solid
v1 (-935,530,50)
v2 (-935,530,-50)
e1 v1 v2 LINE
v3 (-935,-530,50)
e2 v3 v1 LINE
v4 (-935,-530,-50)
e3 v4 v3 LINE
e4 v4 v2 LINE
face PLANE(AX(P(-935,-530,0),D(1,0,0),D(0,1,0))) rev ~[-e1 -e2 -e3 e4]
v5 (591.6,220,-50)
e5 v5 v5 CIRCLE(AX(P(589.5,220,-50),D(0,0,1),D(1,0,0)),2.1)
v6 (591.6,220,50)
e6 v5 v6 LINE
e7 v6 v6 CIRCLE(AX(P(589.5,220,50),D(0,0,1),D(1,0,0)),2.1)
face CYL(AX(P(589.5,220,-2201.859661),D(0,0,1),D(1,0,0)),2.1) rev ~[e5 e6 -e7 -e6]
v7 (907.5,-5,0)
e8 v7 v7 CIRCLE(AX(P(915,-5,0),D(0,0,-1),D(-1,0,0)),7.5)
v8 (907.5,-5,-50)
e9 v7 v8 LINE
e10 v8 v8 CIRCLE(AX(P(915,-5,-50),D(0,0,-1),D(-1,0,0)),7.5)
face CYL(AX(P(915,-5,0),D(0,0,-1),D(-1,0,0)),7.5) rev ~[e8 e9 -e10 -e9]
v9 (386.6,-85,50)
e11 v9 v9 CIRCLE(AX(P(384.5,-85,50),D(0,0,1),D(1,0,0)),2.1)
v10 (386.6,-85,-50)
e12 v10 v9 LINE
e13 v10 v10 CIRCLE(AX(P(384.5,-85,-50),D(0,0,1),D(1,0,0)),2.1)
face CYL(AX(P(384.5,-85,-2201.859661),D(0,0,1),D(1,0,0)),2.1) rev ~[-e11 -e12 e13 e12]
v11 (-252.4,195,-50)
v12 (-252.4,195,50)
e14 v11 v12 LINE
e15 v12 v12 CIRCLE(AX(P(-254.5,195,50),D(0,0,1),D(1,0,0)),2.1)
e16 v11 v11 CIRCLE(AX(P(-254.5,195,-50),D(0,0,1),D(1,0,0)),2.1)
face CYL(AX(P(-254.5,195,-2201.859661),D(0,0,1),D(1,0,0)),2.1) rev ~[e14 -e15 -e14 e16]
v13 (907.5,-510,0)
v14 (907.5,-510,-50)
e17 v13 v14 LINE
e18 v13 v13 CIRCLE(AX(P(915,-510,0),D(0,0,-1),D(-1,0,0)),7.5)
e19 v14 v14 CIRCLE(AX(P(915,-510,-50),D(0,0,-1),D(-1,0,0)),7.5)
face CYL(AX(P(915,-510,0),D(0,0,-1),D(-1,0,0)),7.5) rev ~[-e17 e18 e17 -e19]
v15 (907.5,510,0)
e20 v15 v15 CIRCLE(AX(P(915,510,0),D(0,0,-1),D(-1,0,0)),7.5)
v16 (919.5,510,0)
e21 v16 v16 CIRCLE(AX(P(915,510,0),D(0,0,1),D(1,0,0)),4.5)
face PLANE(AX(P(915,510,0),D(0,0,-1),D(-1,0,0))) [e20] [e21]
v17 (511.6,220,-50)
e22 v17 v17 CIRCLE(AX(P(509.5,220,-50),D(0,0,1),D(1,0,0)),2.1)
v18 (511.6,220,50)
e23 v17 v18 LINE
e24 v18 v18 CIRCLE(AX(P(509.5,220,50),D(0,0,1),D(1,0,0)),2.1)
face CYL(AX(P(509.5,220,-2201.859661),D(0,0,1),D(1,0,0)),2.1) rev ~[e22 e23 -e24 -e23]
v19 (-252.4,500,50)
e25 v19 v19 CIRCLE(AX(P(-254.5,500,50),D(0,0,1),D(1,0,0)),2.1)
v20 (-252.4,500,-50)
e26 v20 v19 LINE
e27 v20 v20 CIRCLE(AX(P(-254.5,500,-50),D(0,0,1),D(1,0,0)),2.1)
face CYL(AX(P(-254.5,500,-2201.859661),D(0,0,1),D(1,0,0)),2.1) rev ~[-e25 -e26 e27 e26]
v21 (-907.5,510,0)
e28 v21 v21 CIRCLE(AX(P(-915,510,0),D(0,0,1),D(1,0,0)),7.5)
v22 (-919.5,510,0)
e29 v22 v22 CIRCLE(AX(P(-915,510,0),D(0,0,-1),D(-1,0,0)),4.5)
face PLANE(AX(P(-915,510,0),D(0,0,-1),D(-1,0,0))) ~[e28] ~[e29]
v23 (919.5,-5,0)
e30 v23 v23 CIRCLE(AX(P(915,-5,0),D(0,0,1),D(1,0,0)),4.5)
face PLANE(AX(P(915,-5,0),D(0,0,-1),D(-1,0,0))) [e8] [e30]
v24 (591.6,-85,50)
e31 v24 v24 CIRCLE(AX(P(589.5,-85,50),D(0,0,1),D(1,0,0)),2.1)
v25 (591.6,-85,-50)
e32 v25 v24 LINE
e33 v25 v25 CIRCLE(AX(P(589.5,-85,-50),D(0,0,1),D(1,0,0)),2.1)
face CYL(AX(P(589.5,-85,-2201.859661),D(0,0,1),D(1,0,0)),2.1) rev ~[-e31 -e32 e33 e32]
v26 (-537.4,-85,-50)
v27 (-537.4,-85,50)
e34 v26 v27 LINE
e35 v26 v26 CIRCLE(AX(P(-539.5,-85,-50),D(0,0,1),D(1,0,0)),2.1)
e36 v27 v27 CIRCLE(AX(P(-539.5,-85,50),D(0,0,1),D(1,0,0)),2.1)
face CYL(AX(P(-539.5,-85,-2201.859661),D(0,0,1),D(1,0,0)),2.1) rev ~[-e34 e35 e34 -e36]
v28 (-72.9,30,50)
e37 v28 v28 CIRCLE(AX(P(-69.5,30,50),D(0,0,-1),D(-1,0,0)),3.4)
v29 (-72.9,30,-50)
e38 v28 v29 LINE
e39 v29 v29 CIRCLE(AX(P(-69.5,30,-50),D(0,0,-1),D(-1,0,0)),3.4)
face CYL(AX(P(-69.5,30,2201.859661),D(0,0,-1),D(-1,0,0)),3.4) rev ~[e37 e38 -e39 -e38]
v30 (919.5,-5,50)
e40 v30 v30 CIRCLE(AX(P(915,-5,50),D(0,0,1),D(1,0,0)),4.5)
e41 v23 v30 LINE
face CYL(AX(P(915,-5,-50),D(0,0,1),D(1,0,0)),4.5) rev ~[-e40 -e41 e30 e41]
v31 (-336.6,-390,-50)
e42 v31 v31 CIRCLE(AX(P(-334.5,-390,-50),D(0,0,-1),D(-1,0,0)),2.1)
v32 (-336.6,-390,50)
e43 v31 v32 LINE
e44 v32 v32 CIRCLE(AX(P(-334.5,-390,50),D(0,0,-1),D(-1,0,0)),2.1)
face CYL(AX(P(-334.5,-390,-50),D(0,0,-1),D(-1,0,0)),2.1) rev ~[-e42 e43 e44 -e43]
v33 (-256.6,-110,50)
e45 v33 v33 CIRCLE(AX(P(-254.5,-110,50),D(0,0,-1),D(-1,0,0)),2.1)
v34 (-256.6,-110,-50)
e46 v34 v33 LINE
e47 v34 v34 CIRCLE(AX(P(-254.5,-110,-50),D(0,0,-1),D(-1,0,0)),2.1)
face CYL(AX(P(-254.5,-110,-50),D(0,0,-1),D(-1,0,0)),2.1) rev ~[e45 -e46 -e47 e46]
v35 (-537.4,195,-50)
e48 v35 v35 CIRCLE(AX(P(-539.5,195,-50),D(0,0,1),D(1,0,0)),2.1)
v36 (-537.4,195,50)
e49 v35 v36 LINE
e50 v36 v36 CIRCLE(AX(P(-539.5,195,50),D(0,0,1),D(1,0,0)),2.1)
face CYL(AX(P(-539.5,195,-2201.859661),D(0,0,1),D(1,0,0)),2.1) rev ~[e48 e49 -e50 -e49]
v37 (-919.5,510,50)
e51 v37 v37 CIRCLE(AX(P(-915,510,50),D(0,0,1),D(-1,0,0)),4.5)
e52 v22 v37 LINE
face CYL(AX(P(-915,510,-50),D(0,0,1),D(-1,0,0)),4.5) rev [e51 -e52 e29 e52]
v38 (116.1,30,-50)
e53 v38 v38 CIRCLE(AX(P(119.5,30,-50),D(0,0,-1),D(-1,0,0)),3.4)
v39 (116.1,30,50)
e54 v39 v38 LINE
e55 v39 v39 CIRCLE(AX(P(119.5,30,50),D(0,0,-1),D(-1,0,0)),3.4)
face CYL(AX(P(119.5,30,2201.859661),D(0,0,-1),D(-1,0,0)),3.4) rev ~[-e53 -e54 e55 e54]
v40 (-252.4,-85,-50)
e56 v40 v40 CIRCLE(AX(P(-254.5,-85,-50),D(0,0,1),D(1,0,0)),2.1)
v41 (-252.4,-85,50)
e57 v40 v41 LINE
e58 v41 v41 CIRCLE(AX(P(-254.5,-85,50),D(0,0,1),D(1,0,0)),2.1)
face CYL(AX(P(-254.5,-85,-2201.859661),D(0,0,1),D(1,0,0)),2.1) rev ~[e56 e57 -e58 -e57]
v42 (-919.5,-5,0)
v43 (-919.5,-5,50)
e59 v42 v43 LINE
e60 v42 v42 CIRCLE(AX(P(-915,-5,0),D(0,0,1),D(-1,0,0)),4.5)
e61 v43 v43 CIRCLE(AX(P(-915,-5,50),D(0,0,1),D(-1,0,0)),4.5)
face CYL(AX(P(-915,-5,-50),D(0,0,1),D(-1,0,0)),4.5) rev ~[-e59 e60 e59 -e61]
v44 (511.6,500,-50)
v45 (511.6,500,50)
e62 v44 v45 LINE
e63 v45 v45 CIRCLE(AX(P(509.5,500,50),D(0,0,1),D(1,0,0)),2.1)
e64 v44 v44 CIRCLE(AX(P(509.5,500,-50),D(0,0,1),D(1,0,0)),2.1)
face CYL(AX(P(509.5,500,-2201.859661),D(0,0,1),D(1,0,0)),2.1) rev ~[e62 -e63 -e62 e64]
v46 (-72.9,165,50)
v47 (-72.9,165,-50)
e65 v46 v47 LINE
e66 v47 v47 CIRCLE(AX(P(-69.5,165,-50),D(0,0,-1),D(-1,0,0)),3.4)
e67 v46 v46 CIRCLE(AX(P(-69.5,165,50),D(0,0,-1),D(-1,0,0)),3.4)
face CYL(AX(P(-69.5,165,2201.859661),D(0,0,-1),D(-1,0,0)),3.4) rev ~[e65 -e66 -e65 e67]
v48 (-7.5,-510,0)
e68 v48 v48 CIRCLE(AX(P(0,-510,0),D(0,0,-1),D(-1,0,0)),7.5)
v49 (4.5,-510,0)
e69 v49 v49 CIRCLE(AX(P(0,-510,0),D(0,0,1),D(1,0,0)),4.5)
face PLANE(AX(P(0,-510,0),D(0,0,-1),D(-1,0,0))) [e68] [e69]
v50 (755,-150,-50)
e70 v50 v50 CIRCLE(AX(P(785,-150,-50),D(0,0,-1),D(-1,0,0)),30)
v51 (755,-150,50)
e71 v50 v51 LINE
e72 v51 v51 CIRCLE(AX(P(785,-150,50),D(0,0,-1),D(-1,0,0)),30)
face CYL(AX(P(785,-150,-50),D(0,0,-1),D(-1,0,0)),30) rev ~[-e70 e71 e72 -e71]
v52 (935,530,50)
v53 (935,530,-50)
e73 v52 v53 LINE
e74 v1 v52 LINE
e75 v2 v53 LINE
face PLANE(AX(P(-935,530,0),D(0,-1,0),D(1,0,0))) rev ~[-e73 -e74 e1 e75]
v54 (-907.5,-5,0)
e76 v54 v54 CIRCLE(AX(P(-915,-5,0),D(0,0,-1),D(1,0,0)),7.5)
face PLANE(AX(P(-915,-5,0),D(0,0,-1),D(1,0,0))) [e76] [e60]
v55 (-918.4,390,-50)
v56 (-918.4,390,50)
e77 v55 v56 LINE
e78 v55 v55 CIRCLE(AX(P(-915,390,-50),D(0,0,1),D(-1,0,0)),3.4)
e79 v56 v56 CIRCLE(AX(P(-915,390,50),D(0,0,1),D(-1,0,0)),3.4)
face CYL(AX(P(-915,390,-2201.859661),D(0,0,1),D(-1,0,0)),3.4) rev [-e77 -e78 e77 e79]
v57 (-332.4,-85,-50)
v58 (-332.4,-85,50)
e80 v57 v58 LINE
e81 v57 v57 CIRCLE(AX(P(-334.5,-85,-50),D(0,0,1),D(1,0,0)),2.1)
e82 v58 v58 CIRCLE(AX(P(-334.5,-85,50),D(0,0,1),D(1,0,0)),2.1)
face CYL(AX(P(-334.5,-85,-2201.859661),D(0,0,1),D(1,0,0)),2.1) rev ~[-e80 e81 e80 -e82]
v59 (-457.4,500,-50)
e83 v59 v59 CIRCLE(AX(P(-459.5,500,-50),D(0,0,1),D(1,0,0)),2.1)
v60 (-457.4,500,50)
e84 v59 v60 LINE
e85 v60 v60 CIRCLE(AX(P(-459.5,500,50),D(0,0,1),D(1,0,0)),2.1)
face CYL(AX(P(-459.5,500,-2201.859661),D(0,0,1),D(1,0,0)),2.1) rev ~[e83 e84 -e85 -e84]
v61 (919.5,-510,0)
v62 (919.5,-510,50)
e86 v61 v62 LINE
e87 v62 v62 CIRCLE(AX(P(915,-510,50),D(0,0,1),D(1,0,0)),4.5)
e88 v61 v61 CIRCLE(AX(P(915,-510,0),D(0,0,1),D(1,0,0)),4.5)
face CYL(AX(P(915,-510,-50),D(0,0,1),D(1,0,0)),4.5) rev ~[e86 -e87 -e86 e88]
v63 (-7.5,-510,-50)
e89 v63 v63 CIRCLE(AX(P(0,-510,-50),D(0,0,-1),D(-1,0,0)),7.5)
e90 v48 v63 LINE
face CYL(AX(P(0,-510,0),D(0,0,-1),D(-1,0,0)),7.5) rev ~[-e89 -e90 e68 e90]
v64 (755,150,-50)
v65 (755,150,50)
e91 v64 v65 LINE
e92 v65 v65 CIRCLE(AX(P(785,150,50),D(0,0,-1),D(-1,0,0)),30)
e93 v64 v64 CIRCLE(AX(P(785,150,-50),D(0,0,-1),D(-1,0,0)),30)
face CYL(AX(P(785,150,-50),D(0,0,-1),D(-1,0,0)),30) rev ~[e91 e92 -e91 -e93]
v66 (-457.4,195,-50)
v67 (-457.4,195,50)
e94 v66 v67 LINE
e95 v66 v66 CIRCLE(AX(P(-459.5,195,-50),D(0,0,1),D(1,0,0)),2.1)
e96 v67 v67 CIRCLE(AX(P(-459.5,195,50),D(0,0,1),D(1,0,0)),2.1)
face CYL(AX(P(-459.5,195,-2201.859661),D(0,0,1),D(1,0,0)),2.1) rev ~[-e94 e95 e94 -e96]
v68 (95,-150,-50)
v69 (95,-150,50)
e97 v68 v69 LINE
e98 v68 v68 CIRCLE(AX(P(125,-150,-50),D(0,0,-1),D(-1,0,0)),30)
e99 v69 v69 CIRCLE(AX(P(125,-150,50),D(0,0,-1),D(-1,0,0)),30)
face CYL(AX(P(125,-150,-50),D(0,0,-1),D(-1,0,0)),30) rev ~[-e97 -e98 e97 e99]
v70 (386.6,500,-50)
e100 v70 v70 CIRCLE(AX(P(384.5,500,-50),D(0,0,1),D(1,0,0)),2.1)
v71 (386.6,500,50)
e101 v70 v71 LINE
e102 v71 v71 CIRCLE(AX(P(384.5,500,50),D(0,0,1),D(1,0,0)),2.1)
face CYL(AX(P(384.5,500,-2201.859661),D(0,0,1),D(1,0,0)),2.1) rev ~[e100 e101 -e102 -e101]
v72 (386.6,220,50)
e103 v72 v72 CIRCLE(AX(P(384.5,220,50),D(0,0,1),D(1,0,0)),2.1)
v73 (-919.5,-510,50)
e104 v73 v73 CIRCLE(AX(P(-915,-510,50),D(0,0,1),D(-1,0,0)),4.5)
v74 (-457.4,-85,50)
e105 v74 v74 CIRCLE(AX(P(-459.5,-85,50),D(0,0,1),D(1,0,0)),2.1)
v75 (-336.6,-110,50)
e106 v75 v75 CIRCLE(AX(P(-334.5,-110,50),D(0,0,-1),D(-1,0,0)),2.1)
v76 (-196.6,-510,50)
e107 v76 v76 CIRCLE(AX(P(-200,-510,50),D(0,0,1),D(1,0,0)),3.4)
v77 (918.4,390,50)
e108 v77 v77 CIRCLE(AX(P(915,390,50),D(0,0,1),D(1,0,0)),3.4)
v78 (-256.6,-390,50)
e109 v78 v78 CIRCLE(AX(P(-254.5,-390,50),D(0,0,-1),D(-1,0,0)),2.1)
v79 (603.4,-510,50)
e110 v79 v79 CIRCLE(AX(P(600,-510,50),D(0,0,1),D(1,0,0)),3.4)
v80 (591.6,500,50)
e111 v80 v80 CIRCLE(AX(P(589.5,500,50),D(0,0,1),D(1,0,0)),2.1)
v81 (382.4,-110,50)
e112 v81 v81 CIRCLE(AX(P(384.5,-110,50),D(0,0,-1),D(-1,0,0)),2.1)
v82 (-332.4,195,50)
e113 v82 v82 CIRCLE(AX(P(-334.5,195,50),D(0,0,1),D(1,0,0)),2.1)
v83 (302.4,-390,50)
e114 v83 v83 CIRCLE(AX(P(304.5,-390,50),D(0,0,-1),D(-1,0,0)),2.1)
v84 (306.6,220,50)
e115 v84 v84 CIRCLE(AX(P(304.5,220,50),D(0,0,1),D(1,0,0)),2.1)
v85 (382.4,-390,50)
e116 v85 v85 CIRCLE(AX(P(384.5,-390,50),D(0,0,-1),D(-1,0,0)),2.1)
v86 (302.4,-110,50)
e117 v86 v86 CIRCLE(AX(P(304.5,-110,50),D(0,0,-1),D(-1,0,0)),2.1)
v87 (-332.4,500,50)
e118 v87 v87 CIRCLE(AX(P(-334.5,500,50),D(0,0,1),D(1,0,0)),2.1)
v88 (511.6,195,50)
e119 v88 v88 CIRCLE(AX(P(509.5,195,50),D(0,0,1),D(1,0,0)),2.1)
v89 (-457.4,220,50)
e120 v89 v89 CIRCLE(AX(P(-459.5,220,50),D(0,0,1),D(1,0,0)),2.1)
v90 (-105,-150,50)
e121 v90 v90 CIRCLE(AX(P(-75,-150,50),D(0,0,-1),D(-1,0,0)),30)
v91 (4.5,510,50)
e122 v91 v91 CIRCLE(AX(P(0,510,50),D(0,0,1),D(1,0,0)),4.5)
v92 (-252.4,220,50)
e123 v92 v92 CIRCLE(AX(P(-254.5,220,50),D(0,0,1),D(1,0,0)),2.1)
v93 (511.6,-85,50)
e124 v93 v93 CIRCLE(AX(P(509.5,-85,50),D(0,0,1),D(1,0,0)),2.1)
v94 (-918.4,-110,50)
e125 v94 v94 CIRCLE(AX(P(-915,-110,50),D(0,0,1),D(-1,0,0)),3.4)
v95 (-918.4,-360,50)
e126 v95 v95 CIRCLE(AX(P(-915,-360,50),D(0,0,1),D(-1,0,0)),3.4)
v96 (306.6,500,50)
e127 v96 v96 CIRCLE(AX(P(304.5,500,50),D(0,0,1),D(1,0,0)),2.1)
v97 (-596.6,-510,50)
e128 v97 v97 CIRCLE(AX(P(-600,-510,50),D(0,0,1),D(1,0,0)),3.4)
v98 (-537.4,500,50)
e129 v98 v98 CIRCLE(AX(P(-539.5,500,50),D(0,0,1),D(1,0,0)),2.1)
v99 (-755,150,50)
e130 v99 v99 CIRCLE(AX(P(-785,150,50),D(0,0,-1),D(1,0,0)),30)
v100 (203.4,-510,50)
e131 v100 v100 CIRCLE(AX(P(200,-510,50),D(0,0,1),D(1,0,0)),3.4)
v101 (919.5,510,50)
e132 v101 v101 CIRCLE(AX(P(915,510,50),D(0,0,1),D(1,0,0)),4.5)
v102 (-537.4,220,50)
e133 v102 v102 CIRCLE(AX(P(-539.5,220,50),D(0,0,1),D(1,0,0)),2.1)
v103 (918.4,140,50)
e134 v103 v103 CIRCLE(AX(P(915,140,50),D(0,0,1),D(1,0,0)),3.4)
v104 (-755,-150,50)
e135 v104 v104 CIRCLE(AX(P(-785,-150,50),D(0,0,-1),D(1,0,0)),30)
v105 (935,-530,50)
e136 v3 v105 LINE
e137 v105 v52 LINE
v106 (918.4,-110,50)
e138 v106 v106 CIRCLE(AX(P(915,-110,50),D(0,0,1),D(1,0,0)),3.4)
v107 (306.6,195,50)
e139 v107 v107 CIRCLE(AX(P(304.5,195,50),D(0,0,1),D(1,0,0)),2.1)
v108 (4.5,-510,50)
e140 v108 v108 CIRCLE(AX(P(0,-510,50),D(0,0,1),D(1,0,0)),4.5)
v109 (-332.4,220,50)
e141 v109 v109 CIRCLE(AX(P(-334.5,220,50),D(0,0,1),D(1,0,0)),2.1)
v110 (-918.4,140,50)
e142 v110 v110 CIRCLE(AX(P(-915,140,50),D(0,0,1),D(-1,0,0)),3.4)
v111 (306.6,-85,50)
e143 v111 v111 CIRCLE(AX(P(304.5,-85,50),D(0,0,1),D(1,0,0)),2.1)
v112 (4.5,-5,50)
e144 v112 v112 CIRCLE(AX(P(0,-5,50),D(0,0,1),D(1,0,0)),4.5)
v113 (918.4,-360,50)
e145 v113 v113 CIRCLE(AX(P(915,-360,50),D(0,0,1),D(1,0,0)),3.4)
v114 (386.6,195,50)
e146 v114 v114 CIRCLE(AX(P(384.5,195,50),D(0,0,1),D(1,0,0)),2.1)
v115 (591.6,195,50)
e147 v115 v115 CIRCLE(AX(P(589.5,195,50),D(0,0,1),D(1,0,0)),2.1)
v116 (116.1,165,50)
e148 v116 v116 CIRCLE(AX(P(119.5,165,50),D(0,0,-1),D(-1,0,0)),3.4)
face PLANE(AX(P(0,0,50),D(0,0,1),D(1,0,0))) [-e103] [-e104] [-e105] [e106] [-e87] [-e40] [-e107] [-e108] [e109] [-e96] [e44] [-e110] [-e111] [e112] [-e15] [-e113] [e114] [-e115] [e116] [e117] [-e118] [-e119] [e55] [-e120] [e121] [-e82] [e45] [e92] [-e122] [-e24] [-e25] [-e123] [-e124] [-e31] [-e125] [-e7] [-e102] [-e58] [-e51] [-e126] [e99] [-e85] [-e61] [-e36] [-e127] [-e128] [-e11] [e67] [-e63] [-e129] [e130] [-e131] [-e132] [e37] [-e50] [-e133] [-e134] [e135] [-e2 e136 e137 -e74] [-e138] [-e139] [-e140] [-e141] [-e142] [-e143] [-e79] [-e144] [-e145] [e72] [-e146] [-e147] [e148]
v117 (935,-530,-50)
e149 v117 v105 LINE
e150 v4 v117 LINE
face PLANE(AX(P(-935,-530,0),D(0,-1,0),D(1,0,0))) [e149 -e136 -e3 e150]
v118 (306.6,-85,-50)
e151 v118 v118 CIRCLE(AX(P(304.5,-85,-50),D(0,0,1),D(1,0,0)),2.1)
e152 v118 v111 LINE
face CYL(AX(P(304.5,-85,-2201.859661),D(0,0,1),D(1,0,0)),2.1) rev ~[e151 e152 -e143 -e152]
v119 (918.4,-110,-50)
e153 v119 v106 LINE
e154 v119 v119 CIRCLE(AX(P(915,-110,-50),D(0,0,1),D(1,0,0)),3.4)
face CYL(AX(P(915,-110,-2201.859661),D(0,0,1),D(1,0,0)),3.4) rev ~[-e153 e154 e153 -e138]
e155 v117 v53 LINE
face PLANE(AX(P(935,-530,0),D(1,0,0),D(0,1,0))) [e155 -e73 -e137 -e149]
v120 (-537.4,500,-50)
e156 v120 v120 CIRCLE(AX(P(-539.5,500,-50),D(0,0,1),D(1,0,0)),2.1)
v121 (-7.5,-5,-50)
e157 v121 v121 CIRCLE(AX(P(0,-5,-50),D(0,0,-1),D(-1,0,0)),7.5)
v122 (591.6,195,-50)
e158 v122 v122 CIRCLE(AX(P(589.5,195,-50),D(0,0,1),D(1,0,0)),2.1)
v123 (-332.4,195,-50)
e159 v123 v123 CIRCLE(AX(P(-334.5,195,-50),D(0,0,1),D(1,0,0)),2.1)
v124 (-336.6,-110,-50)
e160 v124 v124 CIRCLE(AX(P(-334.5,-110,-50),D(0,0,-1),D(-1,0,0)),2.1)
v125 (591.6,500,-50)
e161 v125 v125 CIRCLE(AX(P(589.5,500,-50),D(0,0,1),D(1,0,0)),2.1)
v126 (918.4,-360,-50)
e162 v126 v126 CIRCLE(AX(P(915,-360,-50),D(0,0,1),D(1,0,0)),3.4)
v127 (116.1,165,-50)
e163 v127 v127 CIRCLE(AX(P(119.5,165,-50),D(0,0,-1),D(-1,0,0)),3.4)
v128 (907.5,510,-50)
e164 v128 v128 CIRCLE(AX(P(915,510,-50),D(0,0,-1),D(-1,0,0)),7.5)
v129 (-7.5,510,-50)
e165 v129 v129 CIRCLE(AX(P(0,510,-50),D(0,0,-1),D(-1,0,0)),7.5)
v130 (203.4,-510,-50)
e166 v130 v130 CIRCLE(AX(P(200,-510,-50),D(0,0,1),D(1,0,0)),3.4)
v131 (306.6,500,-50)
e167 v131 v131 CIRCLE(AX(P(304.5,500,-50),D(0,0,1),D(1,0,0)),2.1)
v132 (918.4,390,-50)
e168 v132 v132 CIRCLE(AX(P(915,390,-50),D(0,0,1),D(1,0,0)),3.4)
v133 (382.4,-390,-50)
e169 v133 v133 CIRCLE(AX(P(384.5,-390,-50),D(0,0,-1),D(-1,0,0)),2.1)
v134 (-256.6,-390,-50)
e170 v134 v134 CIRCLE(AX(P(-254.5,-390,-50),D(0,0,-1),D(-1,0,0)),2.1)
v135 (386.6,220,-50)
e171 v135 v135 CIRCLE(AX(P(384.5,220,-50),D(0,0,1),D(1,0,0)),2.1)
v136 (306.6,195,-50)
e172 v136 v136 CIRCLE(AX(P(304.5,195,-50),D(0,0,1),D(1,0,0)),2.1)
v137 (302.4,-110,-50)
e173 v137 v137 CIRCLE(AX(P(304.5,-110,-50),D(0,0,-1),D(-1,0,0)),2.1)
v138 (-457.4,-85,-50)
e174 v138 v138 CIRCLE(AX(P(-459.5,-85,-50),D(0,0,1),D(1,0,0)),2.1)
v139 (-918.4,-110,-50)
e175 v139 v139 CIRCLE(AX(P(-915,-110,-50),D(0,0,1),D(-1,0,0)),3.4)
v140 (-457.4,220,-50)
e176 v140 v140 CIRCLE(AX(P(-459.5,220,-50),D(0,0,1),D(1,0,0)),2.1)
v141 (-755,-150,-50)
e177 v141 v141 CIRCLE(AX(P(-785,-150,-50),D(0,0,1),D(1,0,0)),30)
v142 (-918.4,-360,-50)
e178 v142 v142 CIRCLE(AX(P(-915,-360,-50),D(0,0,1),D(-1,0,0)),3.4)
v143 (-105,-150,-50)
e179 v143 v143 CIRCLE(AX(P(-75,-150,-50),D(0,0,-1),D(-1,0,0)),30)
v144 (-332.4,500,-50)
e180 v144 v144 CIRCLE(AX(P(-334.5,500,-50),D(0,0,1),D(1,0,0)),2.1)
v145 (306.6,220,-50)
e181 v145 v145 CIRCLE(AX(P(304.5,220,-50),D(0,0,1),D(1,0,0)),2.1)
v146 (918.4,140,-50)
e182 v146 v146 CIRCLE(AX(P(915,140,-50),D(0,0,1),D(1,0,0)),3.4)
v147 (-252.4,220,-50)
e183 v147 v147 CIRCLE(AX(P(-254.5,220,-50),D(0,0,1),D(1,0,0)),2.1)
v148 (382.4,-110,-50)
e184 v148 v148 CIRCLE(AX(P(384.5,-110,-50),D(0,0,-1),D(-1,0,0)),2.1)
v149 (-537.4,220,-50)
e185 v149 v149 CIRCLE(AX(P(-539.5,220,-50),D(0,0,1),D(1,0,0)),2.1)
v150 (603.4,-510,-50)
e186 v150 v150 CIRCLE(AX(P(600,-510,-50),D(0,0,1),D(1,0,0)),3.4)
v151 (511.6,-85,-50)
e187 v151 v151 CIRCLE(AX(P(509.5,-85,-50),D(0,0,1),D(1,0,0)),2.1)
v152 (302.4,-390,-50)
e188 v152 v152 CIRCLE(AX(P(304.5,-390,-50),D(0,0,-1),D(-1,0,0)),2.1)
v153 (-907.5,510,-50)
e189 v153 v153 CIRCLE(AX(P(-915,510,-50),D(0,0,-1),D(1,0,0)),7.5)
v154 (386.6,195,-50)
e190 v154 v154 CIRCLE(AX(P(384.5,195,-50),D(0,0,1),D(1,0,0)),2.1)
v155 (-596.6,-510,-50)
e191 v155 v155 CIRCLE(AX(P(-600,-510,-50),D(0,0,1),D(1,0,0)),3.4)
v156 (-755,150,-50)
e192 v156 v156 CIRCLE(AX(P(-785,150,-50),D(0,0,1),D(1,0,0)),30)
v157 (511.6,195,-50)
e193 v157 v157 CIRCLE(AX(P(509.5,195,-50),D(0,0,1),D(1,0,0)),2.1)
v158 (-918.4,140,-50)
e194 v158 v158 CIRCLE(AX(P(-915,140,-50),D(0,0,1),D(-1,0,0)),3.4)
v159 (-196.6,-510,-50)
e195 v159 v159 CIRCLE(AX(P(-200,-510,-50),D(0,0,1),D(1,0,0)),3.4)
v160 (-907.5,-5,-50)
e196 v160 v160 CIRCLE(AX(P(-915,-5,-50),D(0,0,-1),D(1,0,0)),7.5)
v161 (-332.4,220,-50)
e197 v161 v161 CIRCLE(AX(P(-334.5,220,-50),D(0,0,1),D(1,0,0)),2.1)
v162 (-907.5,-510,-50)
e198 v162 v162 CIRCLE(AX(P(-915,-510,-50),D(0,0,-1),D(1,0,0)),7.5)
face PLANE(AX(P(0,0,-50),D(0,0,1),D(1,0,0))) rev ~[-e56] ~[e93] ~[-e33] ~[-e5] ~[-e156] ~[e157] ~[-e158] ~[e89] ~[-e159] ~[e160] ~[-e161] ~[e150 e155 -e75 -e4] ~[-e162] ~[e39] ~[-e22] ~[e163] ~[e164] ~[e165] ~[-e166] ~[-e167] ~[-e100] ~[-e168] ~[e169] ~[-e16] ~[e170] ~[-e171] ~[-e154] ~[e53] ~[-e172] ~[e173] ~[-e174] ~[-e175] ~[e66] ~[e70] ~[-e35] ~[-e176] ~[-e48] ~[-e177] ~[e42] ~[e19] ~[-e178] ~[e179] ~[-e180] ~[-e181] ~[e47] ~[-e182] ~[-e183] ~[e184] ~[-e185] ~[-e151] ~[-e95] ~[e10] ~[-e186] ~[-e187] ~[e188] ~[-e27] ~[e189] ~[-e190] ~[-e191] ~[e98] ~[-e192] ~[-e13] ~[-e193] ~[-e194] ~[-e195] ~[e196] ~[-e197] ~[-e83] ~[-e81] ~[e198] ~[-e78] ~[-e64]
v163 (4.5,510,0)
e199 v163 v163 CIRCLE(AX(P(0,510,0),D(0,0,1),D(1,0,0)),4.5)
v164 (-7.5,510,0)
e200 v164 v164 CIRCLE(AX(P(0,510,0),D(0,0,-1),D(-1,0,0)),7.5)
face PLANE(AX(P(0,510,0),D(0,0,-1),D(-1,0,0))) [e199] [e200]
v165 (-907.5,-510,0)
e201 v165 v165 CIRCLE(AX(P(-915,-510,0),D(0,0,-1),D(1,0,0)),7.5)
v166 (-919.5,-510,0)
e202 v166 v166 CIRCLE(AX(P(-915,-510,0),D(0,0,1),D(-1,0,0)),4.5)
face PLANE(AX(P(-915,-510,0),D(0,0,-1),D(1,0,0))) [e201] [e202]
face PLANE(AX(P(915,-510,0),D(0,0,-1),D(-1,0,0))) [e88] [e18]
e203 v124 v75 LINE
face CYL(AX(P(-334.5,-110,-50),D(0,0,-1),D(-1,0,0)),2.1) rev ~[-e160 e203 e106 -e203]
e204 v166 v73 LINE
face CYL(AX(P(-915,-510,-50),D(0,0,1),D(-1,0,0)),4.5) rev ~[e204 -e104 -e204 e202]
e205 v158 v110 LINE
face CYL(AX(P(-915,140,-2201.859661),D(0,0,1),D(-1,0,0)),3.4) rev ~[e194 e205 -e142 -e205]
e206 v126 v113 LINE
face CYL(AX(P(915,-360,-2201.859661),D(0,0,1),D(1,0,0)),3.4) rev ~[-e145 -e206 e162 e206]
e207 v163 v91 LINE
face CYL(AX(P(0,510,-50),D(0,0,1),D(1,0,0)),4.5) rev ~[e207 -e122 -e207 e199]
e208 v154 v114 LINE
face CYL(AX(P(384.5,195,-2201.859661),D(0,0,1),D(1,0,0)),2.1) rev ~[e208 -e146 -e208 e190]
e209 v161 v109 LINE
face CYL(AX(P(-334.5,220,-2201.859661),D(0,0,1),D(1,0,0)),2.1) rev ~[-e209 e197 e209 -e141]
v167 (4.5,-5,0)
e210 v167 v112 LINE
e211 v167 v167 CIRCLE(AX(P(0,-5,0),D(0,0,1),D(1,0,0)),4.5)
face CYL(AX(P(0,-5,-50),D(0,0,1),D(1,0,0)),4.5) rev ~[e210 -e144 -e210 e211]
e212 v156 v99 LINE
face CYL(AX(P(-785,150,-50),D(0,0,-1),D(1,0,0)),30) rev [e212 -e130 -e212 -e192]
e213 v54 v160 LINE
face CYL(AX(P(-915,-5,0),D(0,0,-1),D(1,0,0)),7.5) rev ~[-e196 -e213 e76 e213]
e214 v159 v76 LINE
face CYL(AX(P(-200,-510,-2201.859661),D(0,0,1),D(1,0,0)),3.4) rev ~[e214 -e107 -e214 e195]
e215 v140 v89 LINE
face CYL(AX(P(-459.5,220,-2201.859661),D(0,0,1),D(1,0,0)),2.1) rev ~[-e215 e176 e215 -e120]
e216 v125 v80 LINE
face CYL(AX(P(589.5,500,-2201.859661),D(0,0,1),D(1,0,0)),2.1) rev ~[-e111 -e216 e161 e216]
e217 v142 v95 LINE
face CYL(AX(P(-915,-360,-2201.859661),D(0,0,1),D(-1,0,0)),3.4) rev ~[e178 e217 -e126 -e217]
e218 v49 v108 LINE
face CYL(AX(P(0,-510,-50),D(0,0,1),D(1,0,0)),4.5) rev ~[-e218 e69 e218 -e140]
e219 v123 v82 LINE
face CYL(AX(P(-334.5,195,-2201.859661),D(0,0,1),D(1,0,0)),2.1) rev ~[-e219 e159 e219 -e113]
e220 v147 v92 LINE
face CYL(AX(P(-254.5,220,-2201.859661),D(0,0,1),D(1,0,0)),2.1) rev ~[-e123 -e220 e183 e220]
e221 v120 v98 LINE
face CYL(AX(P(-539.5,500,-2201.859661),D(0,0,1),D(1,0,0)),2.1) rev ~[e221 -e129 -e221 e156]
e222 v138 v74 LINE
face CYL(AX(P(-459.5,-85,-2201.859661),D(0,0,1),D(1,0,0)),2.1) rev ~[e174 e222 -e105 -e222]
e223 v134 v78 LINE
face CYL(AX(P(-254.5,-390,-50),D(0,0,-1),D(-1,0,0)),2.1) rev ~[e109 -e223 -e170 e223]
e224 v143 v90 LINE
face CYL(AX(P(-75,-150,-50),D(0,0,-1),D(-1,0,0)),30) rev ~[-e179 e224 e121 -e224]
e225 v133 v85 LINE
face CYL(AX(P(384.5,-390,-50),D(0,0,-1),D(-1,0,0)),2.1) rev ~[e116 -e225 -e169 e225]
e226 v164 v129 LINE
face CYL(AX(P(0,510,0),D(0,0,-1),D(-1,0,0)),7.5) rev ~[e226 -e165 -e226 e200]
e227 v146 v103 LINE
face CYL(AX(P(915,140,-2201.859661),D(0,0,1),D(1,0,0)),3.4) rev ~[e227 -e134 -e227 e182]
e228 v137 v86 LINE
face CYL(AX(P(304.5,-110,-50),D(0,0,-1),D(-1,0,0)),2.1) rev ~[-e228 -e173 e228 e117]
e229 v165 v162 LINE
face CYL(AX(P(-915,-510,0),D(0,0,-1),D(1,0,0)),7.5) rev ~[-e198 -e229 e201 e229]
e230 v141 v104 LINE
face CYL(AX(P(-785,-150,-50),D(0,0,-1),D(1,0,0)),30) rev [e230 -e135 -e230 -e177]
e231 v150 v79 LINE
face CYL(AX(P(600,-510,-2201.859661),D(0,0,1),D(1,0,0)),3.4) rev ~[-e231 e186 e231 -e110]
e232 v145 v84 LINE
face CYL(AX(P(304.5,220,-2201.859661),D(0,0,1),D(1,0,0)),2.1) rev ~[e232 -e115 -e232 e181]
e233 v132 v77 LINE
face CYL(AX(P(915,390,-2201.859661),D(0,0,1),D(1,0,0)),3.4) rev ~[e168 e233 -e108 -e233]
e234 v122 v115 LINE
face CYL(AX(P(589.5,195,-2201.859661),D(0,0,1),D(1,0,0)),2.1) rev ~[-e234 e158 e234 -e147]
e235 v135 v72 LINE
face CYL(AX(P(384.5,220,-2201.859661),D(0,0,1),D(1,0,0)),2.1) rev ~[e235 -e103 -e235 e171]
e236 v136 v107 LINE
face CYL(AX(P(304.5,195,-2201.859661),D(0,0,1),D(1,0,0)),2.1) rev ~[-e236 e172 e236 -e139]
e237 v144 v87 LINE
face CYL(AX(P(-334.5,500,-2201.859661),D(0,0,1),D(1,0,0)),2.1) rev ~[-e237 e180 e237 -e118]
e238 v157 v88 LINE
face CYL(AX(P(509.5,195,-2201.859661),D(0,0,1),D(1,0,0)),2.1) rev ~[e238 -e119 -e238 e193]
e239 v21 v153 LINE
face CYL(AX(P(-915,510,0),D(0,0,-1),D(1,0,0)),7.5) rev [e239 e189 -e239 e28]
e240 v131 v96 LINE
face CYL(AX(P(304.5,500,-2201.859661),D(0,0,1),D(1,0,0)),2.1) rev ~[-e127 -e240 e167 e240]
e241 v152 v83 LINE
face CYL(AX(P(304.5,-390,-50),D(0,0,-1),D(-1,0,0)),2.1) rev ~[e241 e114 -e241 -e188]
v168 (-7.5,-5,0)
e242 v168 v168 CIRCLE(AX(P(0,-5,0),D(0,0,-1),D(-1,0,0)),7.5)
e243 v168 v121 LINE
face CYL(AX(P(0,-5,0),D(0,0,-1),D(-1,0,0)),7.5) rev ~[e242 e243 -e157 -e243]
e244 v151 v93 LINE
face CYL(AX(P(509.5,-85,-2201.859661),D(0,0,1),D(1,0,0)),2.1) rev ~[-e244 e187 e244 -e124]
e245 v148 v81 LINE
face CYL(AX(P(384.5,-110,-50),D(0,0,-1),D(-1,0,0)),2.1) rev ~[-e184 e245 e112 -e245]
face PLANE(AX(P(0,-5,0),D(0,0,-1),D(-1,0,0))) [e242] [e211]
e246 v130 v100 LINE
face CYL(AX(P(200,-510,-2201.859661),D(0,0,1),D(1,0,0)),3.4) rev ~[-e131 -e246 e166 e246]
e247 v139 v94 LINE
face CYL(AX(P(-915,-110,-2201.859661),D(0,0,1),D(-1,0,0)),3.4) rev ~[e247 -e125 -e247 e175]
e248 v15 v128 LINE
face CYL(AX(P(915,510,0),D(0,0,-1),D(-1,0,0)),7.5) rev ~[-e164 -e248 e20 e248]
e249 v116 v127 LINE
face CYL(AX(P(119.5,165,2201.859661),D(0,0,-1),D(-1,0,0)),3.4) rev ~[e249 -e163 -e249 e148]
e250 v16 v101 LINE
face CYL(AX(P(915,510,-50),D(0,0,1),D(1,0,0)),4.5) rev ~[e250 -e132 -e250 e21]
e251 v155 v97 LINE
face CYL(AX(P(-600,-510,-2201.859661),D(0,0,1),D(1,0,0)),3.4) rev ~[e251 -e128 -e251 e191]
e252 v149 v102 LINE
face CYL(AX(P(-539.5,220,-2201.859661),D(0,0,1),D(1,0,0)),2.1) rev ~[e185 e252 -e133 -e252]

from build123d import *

# Parameters (mm, degrees)
SKETCH_1_W                           = 1870
SKETCH_1_H                           = 1060
EXTRUDE_1_DEPTH                      = 50
HOLE_WIZARD_M8_1_D                   = 6.8
PATTERN_LINEAR_1_COUNT               = 2
PATTERN_LINEAR_1_PITCH               = 135
PATTERN_LINEAR_1_COUNT_DIR2          = 2
PATTERN_LINEAR_1_PITCH_DIR2          = 189
HOLE_WIZARD_2_D                      = 9
HOLE_WIZARD_2_CBORE_D                = 15
HOLE_WIZARD_2_CBORE_DEPTH            = 50
PATTERN_LINEAR_2_COUNT               = 2
PATTERN_LINEAR_2_PITCH               = 515
PATTERN_LINEAR_3_COUNT               = 2
PATTERN_LINEAR_3_PITCH               = 915
PATTERN_LINEAR_3_COPY_1_D            = 9
PATTERN_LINEAR_3_COPY_1_CBORE_D      = 15
PATTERN_LINEAR_3_COPY_1_CBORE_DEPTH  = 50
HOLE_WIZARD_M5_1_D                   = 4.2
PATTERN_LINEAR_5_COUNT               = 2
PATTERN_LINEAR_5_PITCH               = 280
PATTERN_LINEAR_6_COUNT               = 2
PATTERN_LINEAR_6_PITCH               = 305
PATTERN_LINEAR_6_COPY_1_D            = 4.2
PATTERN_LINEAR_7_COUNT               = 2
PATTERN_LINEAR_7_PITCH               = 205
PATTERN_LINEAR_7_COPY_1_D            = 4.2
PATTERN_LINEAR_7_COPY_2_D            = 4.2
PATTERN_LINEAR_7_COPY_3_D            = 4.2
PATTERN_LINEAR_8_COUNT               = 2
PATTERN_LINEAR_8_PITCH               = 844
PATTERN_LINEAR_8_COPY_1_D            = 4.2
PATTERN_LINEAR_8_COPY_2_D            = 4.2
PATTERN_LINEAR_8_COPY_3_D            = 4.2
PATTERN_LINEAR_8_COPY_4_D            = 4.2
PATTERN_LINEAR_8_COPY_5_D            = 4.2
PATTERN_LINEAR_8_COPY_6_D            = 4.2
PATTERN_LINEAR_8_COPY_7_D            = 4.2
SKETCH_10_R                          = 2.1
CUT_EXTRUDE_1_DEPTH                  = 1080.409560825
PATTERN_LINEAR_9_COUNT               = 2
PATTERN_LINEAR_9_PITCH               = 639
SKETCH_12_R                          = 30
CUT_EXTRUDE_2_DEPTH                  = 1080.409560825
MIRROR_2_COPY_1_D                    = 9
MIRROR_2_COPY_1_CBORE_D              = 15
MIRROR_2_COPY_1_CBORE_DEPTH          = 50
SKETCH_13_R                          = 30
CUT_EXTRUDE_3_DEPTH                  = 1080.409560825
HOLE_WIZARD_M8_2_D                   = 6.8
PATTERN_LINEAR_10_COUNT              = 4
PATTERN_LINEAR_10_PITCH              = 250
MIRROR_3_COPY_1_D                    = 6.8
MIRROR_3_COPY_2_D                    = 6.8
MIRROR_3_COPY_3_D                    = 6.8
HOLE_WIZARD_M8_3_D                   = 6.8
PATTERN_LINEAR_11_COUNT              = 4
PATTERN_LINEAR_11_PITCH              = 400
PATTERN_LINEAR_12_COUNT              = 2
PATTERN_LINEAR_12_PITCH              = 1020
PATTERN_LINEAR_13_COPY_1_D           = 9
PATTERN_LINEAR_13_COPY_1_CBORE_D     = 15
PATTERN_LINEAR_13_COPY_1_CBORE_DEPTH = 50
PATTERN_LINEAR_13_COPY_2_D           = 9
PATTERN_LINEAR_13_COPY_2_CBORE_D     = 15
PATTERN_LINEAR_13_COPY_2_CBORE_DEPTH = 50
MIRROR_4_COPY_1_D                    = 9
MIRROR_4_COPY_1_CBORE_D              = 15
MIRROR_4_COPY_1_CBORE_DEPTH          = 50
MIRROR_4_COPY_2_D                    = 9
MIRROR_4_COPY_2_CBORE_D              = 15
MIRROR_4_COPY_2_CBORE_DEPTH          = 50


with BuildPart() as part:
    # 草图1 → 凸台-拉伸1 (new, symmetric)
    with BuildSketch(Plane.XY):
        Rectangle(SKETCH_1_W, SKETCH_1_H)
    extrude(amount=EXTRUDE_1_DEPTH, both=True)

    # M8 螺纹孔1 (through all)
    with Locations(Plane.XY.offset(50)):
        with Locations((-69.5, 30)):
            hole_wizard_m8_1 = Hole(HOLE_WIZARD_M8_1_D / 2)

    # 阵列(线性)1: Hole Wizard M8 _1 2 × 2
    with Locations(*[(j * PATTERN_LINEAR_1_PITCH_DIR2, i * PATTERN_LINEAR_1_PITCH, 0) for i in range(PATTERN_LINEAR_1_COUNT) for j in range(PATTERN_LINEAR_1_COUNT_DIR2) if (i, j) != (0, 0)]):
        add(hole_wizard_m8_1, mode=Mode.SUBTRACT)

    # 打孔尺寸(%根据)内六角圆柱头螺钉的类型2 (through all)
    with Locations(Plane(origin=(0, 0, -50), x_dir=(-1, 0, 0), z_dir=(0, 0, -1))):
        with Locations((-915, 510)):
            hole_wizard_2 = CounterBoreHole(HOLE_WIZARD_2_D / 2, HOLE_WIZARD_2_CBORE_D / 2, HOLE_WIZARD_2_CBORE_DEPTH)

    # 阵列(线性)2: 打孔尺寸(%根据)内六角圆柱头螺钉的类型2 ×2
    with Locations(*[(0, -i * PATTERN_LINEAR_2_PITCH, 0) for i in range(1, PATTERN_LINEAR_2_COUNT)]):
        add(hole_wizard_2, mode=Mode.SUBTRACT)

    # 阵列(线性)3: 打孔尺寸(%根据)内六角圆柱头螺钉的类型2 ×2
    with Locations(*[(-i * PATTERN_LINEAR_3_PITCH, 0, 0) for i in range(1, PATTERN_LINEAR_3_COUNT)]):
        add(hole_wizard_2, mode=Mode.SUBTRACT)

    # 阵列(线性)3 copy 1 (through all)
    with Locations(Plane(origin=(-915, -515, -50), x_dir=(-1, 0, 0), z_dir=(0, 0, -1))):
        with Locations((-915, 510)):
            CounterBoreHole(PATTERN_LINEAR_3_COPY_1_D / 2, PATTERN_LINEAR_3_COPY_1_CBORE_D / 2, PATTERN_LINEAR_3_COPY_1_CBORE_DEPTH)

    # M5 螺纹孔1 (through all)
    with Locations(Plane(origin=(0, 0, -50), x_dir=(-1, 0, 0), z_dir=(0, 0, -1))):
        with Locations((-589.5, 500), (-509.5, 500)):
            hole_wizard_m5_1 = Hole(HOLE_WIZARD_M5_1_D / 2)

    # 阵列(线性)5: M5 螺纹孔1 ×2
    with Locations(*[(0, -i * PATTERN_LINEAR_5_PITCH, 0) for i in range(1, PATTERN_LINEAR_5_COUNT)]):
        add(hole_wizard_m5_1, mode=Mode.SUBTRACT)

    # 阵列(线性)6: M5 螺纹孔1 ×2
    with Locations(*[(0, -i * PATTERN_LINEAR_6_PITCH, 0) for i in range(1, PATTERN_LINEAR_6_COUNT)]):
        add(hole_wizard_m5_1, mode=Mode.SUBTRACT)

    # 阵列(线性)6 copy 1 (through all)
    with Locations(Plane(origin=(0, -585, -50), x_dir=(-1, 0, 0), z_dir=(0, 0, -1))):
        with Locations((-589.5, 500), (-509.5, 500)):
            Hole(PATTERN_LINEAR_6_COPY_1_D / 2)

    # 阵列(线性)7: M5 螺纹孔1 ×2
    with Locations(*[(-i * PATTERN_LINEAR_7_PITCH, 0, 0) for i in range(1, PATTERN_LINEAR_7_COUNT)]):
        add(hole_wizard_m5_1, mode=Mode.SUBTRACT)

    # 阵列(线性)7 copy 1 (through all)
    with Locations(Plane(origin=(-205, -280, -50), x_dir=(-1, 0, 0), z_dir=(0, 0, -1))):
        with Locations((-589.5, 500), (-509.5, 500)):
            Hole(PATTERN_LINEAR_7_COPY_1_D / 2)

    # 阵列(线性)7 copy 2 (through all)
    with Locations(Plane(origin=(-205, -305, -50), x_dir=(-1, 0, 0), z_dir=(0, 0, -1))):
        with Locations((-589.5, 500), (-509.5, 500)):
            Hole(PATTERN_LINEAR_7_COPY_2_D / 2)

    # 阵列(线性)7 copy 3 (through all)
    with Locations(Plane(origin=(-205, -585, -50), x_dir=(-1, 0, 0), z_dir=(0, 0, -1))):
        with Locations((-589.5, 500), (-509.5, 500)):
            Hole(PATTERN_LINEAR_7_COPY_3_D / 2)

    # 阵列(线性)8: M5 螺纹孔1 ×2
    with Locations(*[(-i * PATTERN_LINEAR_8_PITCH, 0, 0) for i in range(1, PATTERN_LINEAR_8_COUNT)]):
        add(hole_wizard_m5_1, mode=Mode.SUBTRACT)

    # 阵列(线性)8 copy 1 (through all)
    with Locations(Plane(origin=(-844, -280, -50), x_dir=(-1, 0, 0), z_dir=(0, 0, -1))):
        with Locations((-589.5, 500), (-509.5, 500)):
            Hole(PATTERN_LINEAR_8_COPY_1_D / 2)

    # 阵列(线性)8 copy 2 (through all)
    with Locations(Plane(origin=(-844, -305, -50), x_dir=(-1, 0, 0), z_dir=(0, 0, -1))):
        with Locations((-589.5, 500), (-509.5, 500)):
            Hole(PATTERN_LINEAR_8_COPY_2_D / 2)

    # 阵列(线性)8 copy 3 (through all)
    with Locations(Plane(origin=(-844, -585, -50), x_dir=(-1, 0, 0), z_dir=(0, 0, -1))):
        with Locations((-589.5, 500), (-509.5, 500)):
            Hole(PATTERN_LINEAR_8_COPY_3_D / 2)

    # 阵列(线性)8 copy 4 (through all)
    with Locations(Plane(origin=(-1049, 0, -50), x_dir=(-1, 0, 0), z_dir=(0, 0, -1))):
        with Locations((-589.5, 500), (-509.5, 500)):
            Hole(PATTERN_LINEAR_8_COPY_4_D / 2)

    # 阵列(线性)8 copy 5 (through all)
    with Locations(Plane(origin=(-1049, -280, -50), x_dir=(-1, 0, 0), z_dir=(0, 0, -1))):
        with Locations((-589.5, 500), (-509.5, 500)):
            Hole(PATTERN_LINEAR_8_COPY_5_D / 2)

    # 阵列(线性)8 copy 6 (through all)
    with Locations(Plane(origin=(-1049, -305, -50), x_dir=(-1, 0, 0), z_dir=(0, 0, -1))):
        with Locations((-589.5, 500), (-509.5, 500)):
            Hole(PATTERN_LINEAR_8_COPY_6_D / 2)

    # 阵列(线性)8 copy 7 (through all)
    with Locations(Plane(origin=(-1049, -585, -50), x_dir=(-1, 0, 0), z_dir=(0, 0, -1))):
        with Locations((-589.5, 500), (-509.5, 500)):
            Hole(PATTERN_LINEAR_8_COPY_7_D / 2)

    # 草图10 → 切除-拉伸1 (cut, through all)
    with BuildSketch(Plane(origin=(0, 0, -50), x_dir=(-1, 0, 0), z_dir=(0, 0, -1))):
        with Locations((-304.5, -390)):
            Circle(SKETCH_10_R)
        with Locations((-384.5, -390)):
            Circle(SKETCH_10_R)
        with Locations((-304.5, -110)):
            Circle(SKETCH_10_R)
        with Locations((-384.5, -110)):
            Circle(SKETCH_10_R)
    cut_extrude_1 = extrude(amount=-CUT_EXTRUDE_1_DEPTH, mode=Mode.SUBTRACT)

    # 阵列(线性)9: 切除-拉伸1 ×2
    with Locations(*[(-i * PATTERN_LINEAR_9_PITCH, 0, 0) for i in range(1, PATTERN_LINEAR_9_COUNT)]):
        add(cut_extrude_1, mode=Mode.SUBTRACT)

    # 草图12 → 切除-拉伸2 (cut, through all)
    with BuildSketch(Plane(origin=(0, 0, -50), x_dir=(-1, 0, 0), z_dir=(0, 0, -1))):
        with Locations((-785, 150)):
            Circle(SKETCH_12_R)
        with Locations((-785, -150)):
            Circle(SKETCH_12_R)
    cut_extrude_2 = extrude(amount=-CUT_EXTRUDE_2_DEPTH, mode=Mode.SUBTRACT)

    # 镜向1: 切除-拉伸2 across plane
    add(cut_extrude_2.mirror(Plane(origin=(0, 0, 0), x_dir=(0, 0, 1), z_dir=(1, 0, 0))), mode=Mode.SUBTRACT)

    # 镜向2: 打孔尺寸(%根据)内六角圆柱头螺钉的类型2 across plane
    add(hole_wizard_2.mirror(Plane(origin=(0, 0, 0), x_dir=(0, 0, 1), z_dir=(1, 0, 0))), mode=Mode.SUBTRACT)

    # 镜向2 copy 1 (through all)
    with Locations(Plane(origin=(0, -515, -50), x_dir=(1, 0, 0), z_dir=(0, 0, -1))):
        with Locations((-915, -510)):
            CounterBoreHole(MIRROR_2_COPY_1_D / 2, MIRROR_2_COPY_1_CBORE_D / 2, MIRROR_2_COPY_1_CBORE_DEPTH)

    # 草图13 → 切除-拉伸3 (cut, through all)
    with BuildSketch(Plane(origin=(0, 0, -50), x_dir=(-1, 0, 0), z_dir=(0, 0, -1))):
        with Locations((-125, -150)):
            Circle(SKETCH_13_R)
        with Locations((75, -150)):
            Circle(SKETCH_13_R)
    extrude(amount=-CUT_EXTRUDE_3_DEPTH, mode=Mode.SUBTRACT)

    # M8 螺纹孔2 (through all)
    with Locations(Plane(origin=(0, 0, -50), x_dir=(-1, 0, 0), z_dir=(0, 0, -1))):
        with Locations((-915, 390)):
            hole_wizard_m8_2 = Hole(HOLE_WIZARD_M8_2_D / 2)

    # 阵列(线性)10: M8 螺纹孔2 ×4
    with Locations(*[(0, -i * PATTERN_LINEAR_10_PITCH, 0) for i in range(1, PATTERN_LINEAR_10_COUNT)]):
        add(hole_wizard_m8_2, mode=Mode.SUBTRACT)

    # 镜向3: M8 螺纹孔2 across plane
    add(hole_wizard_m8_2.mirror(Plane(origin=(0, 0, 0), x_dir=(0, 0, 1), z_dir=(1, 0, 0))), mode=Mode.SUBTRACT)

    # 镜向3 copy 1 (through all)
    with Locations(Plane(origin=(0, -250, -50), x_dir=(1, 0, 0), z_dir=(0, 0, -1))):
        with Locations((-915, -390)):
            Hole(MIRROR_3_COPY_1_D / 2)

    # 镜向3 copy 2 (through all)
    with Locations(Plane(origin=(0, -500, -50), x_dir=(1, 0, 0), z_dir=(0, 0, -1))):
        with Locations((-915, -390)):
            Hole(MIRROR_3_COPY_2_D / 2)

    # 镜向3 copy 3 (through all)
    with Locations(Plane(origin=(0, -750, -50), x_dir=(1, 0, 0), z_dir=(0, 0, -1))):
        with Locations((-915, -390)):
            Hole(MIRROR_3_COPY_3_D / 2)

    # M8 螺纹孔3 (through all)
    with Locations(Plane(origin=(0, 0, -50), x_dir=(-1, 0, 0), z_dir=(0, 0, -1))):
        with Locations((-600, -510)):
            hole_wizard_m8_3 = Hole(HOLE_WIZARD_M8_3_D / 2)

    # 阵列(线性)11: M8 螺纹孔3 ×4
    with Locations(*[(-i * PATTERN_LINEAR_11_PITCH, 0, 0) for i in range(1, PATTERN_LINEAR_11_COUNT)]):
        add(hole_wizard_m8_3, mode=Mode.SUBTRACT)

    # 阵列(线性)12: 打孔尺寸(%根据)内六角圆柱头螺钉的类型2 ×2
    with Locations(*[(0, -i * PATTERN_LINEAR_12_PITCH, 0) for i in range(1, PATTERN_LINEAR_12_COUNT)]):
        add(hole_wizard_2, mode=Mode.SUBTRACT)

    # 阵列(线性)13 copy 1 (through all)
    with Locations(Plane(origin=(-915, -1020, -50), x_dir=(-1, 0, 0), z_dir=(0, 0, -1))):
        with Locations((-915, 510)):
            CounterBoreHole(PATTERN_LINEAR_13_COPY_1_D / 2, PATTERN_LINEAR_13_COPY_1_CBORE_D / 2, PATTERN_LINEAR_13_COPY_1_CBORE_DEPTH)

    # 阵列(线性)13 copy 2 (through all)
    with Locations(Plane(origin=(-915, 0, -50), x_dir=(-1, 0, 0), z_dir=(0, 0, -1))):
        with Locations((-915, 510)):
            CounterBoreHole(PATTERN_LINEAR_13_COPY_2_D / 2, PATTERN_LINEAR_13_COPY_2_CBORE_D / 2, PATTERN_LINEAR_13_COPY_2_CBORE_DEPTH)

    # 镜向4 copy 1 (through all)
    with Locations(Plane(origin=(0, -1020, -50), x_dir=(1, 0, 0), z_dir=(0, 0, -1))):
        with Locations((-915, -510)):
            CounterBoreHole(MIRROR_4_COPY_1_D / 2, MIRROR_4_COPY_1_CBORE_D / 2, MIRROR_4_COPY_1_CBORE_DEPTH)

    # 镜向4 copy 2 (through all)
    with Locations(Plane(origin=(0, 0, -50), x_dir=(1, 0, 0), z_dir=(0, 0, -1))):
        with Locations((-915, -510)):
            CounterBoreHole(MIRROR_4_COPY_2_D / 2, MIRROR_4_COPY_2_CBORE_D / 2, MIRROR_4_COPY_2_CBORE_DEPTH)


solid = part.part
